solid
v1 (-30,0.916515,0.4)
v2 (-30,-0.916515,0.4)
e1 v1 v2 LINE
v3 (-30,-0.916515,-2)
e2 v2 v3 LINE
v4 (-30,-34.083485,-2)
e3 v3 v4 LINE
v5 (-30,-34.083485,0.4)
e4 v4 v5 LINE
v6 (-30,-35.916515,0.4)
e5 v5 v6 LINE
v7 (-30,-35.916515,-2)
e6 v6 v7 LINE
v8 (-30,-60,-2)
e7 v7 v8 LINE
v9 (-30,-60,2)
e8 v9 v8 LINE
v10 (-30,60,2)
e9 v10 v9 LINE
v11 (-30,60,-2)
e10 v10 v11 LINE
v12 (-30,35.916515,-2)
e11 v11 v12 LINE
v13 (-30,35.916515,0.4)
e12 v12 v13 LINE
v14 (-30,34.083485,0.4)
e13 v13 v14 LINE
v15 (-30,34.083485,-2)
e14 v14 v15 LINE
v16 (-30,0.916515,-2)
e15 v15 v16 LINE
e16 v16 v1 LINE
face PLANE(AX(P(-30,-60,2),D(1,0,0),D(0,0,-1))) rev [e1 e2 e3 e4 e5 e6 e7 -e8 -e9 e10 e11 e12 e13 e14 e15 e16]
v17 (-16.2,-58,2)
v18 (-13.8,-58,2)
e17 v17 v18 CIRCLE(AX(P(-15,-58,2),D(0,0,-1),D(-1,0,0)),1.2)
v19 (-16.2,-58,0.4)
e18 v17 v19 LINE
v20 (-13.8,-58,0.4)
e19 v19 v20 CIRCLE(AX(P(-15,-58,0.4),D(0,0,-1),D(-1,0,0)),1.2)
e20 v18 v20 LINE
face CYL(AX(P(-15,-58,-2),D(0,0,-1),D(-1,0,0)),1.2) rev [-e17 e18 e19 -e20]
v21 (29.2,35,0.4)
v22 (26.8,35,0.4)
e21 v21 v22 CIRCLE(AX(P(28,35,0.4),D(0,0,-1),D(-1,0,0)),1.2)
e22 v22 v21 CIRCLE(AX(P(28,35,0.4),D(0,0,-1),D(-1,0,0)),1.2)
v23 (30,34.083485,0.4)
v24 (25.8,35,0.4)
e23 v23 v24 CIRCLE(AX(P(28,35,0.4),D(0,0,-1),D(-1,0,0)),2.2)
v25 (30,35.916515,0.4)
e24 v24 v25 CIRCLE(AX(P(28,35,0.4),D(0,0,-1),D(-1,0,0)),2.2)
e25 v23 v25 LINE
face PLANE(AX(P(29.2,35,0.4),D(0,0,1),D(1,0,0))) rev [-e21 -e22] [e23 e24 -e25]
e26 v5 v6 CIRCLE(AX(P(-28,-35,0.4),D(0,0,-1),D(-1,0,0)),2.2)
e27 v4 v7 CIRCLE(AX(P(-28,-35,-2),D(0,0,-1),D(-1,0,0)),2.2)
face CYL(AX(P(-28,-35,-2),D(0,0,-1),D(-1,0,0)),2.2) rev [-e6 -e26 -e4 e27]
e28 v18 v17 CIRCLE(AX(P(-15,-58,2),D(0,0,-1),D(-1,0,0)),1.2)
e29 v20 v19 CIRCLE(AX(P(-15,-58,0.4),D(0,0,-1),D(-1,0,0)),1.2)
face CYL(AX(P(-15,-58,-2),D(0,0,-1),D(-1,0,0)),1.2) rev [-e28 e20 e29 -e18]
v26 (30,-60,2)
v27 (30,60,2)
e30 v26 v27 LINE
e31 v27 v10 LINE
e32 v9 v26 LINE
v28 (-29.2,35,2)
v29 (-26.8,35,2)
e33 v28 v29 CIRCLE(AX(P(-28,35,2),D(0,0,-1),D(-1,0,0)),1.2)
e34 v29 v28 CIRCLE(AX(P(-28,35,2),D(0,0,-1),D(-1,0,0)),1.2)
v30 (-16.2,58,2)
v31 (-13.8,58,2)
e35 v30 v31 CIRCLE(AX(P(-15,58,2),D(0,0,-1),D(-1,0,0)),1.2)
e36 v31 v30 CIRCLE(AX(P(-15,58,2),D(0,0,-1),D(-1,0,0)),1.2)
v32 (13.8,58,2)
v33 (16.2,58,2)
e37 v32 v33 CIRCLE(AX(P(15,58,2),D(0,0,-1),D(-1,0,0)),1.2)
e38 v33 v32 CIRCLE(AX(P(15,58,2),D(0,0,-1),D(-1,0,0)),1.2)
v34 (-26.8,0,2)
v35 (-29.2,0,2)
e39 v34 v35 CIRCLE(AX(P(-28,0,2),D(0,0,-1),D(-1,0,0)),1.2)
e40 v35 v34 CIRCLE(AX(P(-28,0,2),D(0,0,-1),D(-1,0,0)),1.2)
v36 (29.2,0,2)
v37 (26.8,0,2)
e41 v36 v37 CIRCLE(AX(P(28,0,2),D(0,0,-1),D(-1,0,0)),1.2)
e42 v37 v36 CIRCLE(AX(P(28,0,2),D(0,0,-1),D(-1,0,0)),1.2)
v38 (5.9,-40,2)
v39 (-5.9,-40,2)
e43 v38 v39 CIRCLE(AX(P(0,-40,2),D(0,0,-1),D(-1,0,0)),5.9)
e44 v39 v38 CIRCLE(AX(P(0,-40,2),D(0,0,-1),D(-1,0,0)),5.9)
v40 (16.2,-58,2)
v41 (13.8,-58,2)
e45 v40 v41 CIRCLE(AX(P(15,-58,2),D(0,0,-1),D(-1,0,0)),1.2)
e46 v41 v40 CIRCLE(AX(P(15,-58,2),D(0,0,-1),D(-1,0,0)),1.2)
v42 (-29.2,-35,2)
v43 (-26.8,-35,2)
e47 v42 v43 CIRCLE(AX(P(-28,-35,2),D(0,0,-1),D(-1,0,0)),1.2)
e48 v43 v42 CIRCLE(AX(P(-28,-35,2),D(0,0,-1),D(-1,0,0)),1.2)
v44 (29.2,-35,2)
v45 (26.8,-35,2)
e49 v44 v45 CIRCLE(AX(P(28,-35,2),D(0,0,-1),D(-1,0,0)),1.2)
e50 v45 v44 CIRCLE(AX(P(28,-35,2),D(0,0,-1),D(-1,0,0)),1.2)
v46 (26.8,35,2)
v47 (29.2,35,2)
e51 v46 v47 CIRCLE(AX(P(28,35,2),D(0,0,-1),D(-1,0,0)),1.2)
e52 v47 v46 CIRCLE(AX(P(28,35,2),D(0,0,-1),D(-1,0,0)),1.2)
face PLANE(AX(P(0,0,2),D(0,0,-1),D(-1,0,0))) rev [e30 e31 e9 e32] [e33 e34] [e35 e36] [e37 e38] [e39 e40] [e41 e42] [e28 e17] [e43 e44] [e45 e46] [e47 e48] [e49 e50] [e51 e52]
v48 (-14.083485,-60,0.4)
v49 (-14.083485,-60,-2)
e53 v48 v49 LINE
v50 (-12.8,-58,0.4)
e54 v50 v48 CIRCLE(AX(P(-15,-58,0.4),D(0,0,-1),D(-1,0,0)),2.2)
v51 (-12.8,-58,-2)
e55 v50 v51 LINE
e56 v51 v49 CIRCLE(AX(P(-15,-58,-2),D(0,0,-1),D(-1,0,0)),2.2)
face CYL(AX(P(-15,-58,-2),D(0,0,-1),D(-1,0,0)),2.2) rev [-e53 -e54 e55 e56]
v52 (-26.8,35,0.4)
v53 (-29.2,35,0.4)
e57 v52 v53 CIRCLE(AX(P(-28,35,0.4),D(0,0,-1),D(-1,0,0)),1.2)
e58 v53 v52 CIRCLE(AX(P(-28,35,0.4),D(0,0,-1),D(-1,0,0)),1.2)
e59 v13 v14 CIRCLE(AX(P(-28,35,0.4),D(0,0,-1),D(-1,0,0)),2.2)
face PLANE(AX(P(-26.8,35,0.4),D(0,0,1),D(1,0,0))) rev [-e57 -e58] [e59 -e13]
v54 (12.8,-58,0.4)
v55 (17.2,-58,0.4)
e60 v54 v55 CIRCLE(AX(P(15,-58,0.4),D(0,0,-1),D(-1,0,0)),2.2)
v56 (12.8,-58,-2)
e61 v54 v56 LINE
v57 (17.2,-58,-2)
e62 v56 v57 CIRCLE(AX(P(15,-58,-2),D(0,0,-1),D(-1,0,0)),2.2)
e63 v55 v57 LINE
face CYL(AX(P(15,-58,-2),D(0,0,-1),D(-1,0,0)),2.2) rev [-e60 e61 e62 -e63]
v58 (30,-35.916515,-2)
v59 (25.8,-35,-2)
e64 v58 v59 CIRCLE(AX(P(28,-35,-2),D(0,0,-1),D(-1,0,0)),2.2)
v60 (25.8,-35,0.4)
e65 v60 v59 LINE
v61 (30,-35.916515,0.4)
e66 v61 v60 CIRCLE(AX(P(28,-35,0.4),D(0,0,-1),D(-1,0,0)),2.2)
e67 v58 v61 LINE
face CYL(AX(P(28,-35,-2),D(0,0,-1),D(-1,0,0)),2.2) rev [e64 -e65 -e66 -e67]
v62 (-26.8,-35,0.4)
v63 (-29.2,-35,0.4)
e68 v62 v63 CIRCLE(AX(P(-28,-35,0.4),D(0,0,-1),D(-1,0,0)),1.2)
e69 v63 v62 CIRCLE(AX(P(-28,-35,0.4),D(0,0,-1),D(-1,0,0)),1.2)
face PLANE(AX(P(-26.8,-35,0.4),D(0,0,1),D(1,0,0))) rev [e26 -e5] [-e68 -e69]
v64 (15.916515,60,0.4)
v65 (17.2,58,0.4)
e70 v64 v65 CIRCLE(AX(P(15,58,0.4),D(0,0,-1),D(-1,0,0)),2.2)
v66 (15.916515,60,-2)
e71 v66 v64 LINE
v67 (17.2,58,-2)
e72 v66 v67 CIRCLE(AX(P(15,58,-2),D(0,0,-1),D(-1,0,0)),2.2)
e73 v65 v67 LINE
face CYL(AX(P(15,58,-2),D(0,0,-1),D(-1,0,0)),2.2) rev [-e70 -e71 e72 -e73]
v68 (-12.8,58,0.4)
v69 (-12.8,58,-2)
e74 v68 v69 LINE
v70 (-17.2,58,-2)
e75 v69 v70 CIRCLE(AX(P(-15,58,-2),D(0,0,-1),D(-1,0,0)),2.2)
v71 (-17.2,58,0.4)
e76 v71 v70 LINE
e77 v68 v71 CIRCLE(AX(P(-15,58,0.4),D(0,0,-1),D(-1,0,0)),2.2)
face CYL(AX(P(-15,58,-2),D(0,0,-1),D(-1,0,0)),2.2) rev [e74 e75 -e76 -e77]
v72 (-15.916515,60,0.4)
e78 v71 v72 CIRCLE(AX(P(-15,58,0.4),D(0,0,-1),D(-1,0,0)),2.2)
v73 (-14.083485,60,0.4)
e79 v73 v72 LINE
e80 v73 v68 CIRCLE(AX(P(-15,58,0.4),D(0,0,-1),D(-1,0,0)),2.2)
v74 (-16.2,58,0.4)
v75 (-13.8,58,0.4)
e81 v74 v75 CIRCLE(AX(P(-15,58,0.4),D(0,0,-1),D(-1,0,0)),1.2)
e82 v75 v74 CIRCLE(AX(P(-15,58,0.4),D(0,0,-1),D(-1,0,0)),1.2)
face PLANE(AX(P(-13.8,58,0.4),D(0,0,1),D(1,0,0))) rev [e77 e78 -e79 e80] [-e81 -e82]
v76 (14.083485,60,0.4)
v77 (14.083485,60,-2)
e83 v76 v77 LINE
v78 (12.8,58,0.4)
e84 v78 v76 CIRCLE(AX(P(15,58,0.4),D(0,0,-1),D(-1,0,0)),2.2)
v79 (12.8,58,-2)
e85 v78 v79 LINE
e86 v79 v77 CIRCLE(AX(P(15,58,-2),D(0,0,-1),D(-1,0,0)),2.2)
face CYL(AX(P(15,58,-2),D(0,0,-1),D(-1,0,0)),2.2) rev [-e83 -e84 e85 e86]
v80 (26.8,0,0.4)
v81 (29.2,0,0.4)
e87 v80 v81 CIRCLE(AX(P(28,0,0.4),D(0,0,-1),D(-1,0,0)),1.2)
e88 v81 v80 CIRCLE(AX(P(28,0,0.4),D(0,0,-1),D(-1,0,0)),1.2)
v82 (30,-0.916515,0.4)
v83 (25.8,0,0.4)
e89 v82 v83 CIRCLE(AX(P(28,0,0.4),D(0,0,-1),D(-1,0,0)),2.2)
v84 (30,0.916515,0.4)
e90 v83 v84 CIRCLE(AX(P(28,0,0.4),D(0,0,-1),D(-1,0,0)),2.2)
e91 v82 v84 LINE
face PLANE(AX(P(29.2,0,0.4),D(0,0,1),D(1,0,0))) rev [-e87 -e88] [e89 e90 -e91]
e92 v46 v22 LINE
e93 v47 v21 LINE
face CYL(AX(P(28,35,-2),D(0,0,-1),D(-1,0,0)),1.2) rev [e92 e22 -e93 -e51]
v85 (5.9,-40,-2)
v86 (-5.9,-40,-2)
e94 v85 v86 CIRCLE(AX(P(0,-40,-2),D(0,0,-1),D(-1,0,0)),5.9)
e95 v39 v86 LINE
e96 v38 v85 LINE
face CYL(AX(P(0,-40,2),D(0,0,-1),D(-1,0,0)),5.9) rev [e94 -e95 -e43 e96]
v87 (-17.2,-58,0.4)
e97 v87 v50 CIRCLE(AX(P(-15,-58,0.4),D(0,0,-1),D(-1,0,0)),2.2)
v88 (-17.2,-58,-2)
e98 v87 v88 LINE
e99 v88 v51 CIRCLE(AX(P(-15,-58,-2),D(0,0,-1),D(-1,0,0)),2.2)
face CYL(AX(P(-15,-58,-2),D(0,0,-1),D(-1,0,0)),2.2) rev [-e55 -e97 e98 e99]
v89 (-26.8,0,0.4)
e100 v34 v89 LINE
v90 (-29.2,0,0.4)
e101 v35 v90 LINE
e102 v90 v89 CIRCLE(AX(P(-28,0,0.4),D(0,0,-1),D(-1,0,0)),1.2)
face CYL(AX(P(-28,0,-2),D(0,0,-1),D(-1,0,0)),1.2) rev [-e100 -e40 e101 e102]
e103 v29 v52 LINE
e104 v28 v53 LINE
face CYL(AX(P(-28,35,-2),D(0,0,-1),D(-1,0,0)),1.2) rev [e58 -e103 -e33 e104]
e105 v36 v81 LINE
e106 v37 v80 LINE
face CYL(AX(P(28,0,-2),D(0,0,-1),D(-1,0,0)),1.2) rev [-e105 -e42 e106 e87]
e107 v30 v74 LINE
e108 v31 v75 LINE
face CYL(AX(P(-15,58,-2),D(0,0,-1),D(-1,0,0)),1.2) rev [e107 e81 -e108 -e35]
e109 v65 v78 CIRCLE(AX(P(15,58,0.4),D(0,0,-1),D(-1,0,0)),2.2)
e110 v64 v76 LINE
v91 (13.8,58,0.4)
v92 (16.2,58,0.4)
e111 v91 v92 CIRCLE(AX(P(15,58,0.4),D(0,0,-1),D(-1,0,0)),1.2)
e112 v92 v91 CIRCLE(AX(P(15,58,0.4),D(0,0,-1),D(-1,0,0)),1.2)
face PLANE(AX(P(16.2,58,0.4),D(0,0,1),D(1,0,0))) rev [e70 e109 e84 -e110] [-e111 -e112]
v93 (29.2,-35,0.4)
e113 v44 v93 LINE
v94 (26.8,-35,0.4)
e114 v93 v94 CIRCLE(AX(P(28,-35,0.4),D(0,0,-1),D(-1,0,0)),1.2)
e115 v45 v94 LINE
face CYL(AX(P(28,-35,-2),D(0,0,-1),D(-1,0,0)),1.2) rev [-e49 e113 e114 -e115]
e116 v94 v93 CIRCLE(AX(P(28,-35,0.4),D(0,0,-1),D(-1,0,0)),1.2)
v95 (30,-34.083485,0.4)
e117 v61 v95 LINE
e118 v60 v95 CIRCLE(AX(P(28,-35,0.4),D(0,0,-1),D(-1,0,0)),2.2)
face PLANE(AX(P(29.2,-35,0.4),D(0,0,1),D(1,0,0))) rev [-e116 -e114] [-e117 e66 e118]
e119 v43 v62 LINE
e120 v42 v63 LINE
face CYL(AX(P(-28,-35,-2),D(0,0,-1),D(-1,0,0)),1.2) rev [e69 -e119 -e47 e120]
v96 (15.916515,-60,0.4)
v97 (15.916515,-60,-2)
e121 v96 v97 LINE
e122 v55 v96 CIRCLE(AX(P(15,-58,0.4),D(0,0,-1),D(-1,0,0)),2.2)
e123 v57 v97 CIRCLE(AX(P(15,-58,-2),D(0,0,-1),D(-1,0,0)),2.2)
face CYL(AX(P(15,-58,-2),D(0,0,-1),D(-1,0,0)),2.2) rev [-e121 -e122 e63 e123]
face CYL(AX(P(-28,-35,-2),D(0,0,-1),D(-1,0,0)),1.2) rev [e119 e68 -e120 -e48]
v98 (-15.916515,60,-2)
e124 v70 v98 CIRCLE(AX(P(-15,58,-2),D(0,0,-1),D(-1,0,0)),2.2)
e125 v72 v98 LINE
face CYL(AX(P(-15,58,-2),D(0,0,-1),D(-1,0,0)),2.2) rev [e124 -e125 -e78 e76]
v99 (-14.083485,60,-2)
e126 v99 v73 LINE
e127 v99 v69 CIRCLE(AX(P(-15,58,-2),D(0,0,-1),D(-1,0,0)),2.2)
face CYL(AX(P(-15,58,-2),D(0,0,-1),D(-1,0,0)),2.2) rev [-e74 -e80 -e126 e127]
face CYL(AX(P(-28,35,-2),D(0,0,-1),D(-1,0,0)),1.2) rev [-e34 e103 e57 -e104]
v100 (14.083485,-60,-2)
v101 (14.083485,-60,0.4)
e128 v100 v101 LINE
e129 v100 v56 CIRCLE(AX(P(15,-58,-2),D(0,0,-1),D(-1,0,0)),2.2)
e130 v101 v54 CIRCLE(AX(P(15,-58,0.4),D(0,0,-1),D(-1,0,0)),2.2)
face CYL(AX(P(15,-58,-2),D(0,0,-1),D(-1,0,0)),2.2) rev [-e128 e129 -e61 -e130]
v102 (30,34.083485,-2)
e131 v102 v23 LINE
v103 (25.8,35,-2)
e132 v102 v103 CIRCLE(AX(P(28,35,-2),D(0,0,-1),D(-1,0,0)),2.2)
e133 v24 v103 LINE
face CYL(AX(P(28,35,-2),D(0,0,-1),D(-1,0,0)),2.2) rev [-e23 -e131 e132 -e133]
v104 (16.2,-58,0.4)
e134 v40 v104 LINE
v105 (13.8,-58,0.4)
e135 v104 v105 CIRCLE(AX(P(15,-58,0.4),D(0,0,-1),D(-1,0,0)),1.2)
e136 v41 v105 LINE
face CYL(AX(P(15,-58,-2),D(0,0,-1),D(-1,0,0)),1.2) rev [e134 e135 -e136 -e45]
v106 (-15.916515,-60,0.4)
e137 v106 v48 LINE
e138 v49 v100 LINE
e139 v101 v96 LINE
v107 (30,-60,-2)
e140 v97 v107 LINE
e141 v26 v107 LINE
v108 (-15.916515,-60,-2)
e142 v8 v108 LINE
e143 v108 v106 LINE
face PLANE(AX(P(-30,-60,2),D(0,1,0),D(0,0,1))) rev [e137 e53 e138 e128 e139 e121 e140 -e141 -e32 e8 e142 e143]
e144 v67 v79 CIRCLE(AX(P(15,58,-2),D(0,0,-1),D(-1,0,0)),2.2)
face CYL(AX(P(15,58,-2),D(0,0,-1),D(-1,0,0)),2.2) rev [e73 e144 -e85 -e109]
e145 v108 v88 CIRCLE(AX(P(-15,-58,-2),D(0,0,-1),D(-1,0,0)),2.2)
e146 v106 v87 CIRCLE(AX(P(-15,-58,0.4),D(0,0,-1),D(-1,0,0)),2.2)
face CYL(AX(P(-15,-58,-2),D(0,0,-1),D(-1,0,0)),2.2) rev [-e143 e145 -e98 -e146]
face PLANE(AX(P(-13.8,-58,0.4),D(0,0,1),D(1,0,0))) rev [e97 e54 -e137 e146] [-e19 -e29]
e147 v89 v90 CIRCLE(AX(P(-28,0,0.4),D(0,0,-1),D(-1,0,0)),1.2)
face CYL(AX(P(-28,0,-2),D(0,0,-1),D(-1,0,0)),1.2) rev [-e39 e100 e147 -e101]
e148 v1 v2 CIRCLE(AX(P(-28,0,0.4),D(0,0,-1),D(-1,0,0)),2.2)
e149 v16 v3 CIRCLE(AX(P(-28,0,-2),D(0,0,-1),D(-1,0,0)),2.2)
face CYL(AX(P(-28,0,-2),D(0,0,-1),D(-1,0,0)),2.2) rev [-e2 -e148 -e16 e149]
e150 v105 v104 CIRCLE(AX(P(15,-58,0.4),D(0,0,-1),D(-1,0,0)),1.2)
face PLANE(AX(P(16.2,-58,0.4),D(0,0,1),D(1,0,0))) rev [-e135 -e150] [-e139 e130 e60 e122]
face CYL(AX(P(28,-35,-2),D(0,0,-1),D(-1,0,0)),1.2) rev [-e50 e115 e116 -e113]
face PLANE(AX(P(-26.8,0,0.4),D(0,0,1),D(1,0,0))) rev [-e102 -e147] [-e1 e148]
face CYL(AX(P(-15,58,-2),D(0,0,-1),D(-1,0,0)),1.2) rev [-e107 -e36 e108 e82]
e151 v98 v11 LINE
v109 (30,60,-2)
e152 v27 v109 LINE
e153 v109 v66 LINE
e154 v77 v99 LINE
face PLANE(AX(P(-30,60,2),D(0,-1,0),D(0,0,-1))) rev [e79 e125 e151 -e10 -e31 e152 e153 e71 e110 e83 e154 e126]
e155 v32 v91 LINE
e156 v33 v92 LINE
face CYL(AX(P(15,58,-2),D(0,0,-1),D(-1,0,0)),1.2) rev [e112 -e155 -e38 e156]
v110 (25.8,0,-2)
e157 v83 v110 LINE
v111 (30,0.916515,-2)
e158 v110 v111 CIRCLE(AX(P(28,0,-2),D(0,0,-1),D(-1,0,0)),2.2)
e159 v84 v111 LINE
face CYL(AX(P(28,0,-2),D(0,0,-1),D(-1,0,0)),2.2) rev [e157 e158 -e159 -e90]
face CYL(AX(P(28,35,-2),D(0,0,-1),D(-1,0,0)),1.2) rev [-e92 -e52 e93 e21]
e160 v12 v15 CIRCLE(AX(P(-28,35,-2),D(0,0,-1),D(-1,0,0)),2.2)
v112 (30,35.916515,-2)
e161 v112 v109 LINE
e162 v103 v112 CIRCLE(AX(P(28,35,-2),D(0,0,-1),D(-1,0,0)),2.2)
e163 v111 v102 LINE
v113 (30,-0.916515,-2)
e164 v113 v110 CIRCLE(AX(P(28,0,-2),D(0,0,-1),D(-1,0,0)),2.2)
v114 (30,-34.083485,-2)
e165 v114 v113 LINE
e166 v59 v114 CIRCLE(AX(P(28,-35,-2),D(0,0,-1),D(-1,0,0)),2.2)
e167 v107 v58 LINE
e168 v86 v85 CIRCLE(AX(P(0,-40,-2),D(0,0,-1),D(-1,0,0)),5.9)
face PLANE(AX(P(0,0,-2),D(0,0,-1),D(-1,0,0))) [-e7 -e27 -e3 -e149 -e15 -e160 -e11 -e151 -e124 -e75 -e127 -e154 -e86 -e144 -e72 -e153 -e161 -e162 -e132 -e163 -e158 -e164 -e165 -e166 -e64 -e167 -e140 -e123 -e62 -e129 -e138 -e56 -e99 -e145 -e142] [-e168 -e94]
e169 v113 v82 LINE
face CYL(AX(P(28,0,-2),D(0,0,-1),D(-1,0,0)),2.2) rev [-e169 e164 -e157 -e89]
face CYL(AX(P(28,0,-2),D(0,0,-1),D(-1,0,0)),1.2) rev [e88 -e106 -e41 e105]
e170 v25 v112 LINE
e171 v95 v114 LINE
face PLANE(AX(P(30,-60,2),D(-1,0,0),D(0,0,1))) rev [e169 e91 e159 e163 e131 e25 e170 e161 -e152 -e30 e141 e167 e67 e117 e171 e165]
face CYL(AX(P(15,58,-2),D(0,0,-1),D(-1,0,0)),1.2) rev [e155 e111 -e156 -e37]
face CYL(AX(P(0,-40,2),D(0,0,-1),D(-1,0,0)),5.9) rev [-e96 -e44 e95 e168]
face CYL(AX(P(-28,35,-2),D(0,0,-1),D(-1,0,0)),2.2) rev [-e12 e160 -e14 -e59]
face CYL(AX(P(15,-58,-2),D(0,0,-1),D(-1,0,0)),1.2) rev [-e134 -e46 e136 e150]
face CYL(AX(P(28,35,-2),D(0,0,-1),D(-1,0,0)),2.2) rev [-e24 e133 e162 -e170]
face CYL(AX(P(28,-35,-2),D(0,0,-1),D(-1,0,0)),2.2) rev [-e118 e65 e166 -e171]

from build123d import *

# Parameters (mm, degrees)
SKETCH_1_W                   = 60
SKETCH_1_H                   = 120
EXTRUDE_1_DEPTH              = 2
HOLE_WIZARD_M2_1_D           = 2.4
HOLE_WIZARD_M2_1_CBORE_D     = 4.4
HOLE_WIZARD_M2_1_CBORE_DEPTH = 2.4
SKETCH_7_R                   = 5.9
CUT_EXTRUDE_2_DEPTH          = 68.201190466


with BuildPart() as part:
    # 草图1 → 凸台-拉伸1 (new, symmetric)
    with BuildSketch(Plane.XY):
        Rectangle(SKETCH_1_W, SKETCH_1_H)
    extrude(amount=EXTRUDE_1_DEPTH, both=True)

    # M2 六角凹头螺钉的柱形沉头孔1 (through all)
    with Locations(Plane(origin=(0, 0, -2), x_dir=(-1, 0, 0), z_dir=(0, 0, -1))):
        with Locations((-15, -58), (-28, 0), (28, 0), (-15, 58), (15, 58), (-28, 35), (28, 35), (-28, -35), (28, -35), (15, -58)):
            CounterBoreHole(HOLE_WIZARD_M2_1_D / 2, HOLE_WIZARD_M2_1_CBORE_D / 2, HOLE_WIZARD_M2_1_CBORE_DEPTH)

    # 草图7 → 切除-拉伸2 (cut, through all)
    with BuildSketch(Plane(origin=(0, 0, -2), x_dir=(-1, 0, 0), z_dir=(0, 0, -1))):
        with Locations((0, -40)):
            Circle(SKETCH_7_R)
    extrude(amount=-CUT_EXTRUDE_2_DEPTH, mode=Mode.SUBTRACT)


solid = part.part
